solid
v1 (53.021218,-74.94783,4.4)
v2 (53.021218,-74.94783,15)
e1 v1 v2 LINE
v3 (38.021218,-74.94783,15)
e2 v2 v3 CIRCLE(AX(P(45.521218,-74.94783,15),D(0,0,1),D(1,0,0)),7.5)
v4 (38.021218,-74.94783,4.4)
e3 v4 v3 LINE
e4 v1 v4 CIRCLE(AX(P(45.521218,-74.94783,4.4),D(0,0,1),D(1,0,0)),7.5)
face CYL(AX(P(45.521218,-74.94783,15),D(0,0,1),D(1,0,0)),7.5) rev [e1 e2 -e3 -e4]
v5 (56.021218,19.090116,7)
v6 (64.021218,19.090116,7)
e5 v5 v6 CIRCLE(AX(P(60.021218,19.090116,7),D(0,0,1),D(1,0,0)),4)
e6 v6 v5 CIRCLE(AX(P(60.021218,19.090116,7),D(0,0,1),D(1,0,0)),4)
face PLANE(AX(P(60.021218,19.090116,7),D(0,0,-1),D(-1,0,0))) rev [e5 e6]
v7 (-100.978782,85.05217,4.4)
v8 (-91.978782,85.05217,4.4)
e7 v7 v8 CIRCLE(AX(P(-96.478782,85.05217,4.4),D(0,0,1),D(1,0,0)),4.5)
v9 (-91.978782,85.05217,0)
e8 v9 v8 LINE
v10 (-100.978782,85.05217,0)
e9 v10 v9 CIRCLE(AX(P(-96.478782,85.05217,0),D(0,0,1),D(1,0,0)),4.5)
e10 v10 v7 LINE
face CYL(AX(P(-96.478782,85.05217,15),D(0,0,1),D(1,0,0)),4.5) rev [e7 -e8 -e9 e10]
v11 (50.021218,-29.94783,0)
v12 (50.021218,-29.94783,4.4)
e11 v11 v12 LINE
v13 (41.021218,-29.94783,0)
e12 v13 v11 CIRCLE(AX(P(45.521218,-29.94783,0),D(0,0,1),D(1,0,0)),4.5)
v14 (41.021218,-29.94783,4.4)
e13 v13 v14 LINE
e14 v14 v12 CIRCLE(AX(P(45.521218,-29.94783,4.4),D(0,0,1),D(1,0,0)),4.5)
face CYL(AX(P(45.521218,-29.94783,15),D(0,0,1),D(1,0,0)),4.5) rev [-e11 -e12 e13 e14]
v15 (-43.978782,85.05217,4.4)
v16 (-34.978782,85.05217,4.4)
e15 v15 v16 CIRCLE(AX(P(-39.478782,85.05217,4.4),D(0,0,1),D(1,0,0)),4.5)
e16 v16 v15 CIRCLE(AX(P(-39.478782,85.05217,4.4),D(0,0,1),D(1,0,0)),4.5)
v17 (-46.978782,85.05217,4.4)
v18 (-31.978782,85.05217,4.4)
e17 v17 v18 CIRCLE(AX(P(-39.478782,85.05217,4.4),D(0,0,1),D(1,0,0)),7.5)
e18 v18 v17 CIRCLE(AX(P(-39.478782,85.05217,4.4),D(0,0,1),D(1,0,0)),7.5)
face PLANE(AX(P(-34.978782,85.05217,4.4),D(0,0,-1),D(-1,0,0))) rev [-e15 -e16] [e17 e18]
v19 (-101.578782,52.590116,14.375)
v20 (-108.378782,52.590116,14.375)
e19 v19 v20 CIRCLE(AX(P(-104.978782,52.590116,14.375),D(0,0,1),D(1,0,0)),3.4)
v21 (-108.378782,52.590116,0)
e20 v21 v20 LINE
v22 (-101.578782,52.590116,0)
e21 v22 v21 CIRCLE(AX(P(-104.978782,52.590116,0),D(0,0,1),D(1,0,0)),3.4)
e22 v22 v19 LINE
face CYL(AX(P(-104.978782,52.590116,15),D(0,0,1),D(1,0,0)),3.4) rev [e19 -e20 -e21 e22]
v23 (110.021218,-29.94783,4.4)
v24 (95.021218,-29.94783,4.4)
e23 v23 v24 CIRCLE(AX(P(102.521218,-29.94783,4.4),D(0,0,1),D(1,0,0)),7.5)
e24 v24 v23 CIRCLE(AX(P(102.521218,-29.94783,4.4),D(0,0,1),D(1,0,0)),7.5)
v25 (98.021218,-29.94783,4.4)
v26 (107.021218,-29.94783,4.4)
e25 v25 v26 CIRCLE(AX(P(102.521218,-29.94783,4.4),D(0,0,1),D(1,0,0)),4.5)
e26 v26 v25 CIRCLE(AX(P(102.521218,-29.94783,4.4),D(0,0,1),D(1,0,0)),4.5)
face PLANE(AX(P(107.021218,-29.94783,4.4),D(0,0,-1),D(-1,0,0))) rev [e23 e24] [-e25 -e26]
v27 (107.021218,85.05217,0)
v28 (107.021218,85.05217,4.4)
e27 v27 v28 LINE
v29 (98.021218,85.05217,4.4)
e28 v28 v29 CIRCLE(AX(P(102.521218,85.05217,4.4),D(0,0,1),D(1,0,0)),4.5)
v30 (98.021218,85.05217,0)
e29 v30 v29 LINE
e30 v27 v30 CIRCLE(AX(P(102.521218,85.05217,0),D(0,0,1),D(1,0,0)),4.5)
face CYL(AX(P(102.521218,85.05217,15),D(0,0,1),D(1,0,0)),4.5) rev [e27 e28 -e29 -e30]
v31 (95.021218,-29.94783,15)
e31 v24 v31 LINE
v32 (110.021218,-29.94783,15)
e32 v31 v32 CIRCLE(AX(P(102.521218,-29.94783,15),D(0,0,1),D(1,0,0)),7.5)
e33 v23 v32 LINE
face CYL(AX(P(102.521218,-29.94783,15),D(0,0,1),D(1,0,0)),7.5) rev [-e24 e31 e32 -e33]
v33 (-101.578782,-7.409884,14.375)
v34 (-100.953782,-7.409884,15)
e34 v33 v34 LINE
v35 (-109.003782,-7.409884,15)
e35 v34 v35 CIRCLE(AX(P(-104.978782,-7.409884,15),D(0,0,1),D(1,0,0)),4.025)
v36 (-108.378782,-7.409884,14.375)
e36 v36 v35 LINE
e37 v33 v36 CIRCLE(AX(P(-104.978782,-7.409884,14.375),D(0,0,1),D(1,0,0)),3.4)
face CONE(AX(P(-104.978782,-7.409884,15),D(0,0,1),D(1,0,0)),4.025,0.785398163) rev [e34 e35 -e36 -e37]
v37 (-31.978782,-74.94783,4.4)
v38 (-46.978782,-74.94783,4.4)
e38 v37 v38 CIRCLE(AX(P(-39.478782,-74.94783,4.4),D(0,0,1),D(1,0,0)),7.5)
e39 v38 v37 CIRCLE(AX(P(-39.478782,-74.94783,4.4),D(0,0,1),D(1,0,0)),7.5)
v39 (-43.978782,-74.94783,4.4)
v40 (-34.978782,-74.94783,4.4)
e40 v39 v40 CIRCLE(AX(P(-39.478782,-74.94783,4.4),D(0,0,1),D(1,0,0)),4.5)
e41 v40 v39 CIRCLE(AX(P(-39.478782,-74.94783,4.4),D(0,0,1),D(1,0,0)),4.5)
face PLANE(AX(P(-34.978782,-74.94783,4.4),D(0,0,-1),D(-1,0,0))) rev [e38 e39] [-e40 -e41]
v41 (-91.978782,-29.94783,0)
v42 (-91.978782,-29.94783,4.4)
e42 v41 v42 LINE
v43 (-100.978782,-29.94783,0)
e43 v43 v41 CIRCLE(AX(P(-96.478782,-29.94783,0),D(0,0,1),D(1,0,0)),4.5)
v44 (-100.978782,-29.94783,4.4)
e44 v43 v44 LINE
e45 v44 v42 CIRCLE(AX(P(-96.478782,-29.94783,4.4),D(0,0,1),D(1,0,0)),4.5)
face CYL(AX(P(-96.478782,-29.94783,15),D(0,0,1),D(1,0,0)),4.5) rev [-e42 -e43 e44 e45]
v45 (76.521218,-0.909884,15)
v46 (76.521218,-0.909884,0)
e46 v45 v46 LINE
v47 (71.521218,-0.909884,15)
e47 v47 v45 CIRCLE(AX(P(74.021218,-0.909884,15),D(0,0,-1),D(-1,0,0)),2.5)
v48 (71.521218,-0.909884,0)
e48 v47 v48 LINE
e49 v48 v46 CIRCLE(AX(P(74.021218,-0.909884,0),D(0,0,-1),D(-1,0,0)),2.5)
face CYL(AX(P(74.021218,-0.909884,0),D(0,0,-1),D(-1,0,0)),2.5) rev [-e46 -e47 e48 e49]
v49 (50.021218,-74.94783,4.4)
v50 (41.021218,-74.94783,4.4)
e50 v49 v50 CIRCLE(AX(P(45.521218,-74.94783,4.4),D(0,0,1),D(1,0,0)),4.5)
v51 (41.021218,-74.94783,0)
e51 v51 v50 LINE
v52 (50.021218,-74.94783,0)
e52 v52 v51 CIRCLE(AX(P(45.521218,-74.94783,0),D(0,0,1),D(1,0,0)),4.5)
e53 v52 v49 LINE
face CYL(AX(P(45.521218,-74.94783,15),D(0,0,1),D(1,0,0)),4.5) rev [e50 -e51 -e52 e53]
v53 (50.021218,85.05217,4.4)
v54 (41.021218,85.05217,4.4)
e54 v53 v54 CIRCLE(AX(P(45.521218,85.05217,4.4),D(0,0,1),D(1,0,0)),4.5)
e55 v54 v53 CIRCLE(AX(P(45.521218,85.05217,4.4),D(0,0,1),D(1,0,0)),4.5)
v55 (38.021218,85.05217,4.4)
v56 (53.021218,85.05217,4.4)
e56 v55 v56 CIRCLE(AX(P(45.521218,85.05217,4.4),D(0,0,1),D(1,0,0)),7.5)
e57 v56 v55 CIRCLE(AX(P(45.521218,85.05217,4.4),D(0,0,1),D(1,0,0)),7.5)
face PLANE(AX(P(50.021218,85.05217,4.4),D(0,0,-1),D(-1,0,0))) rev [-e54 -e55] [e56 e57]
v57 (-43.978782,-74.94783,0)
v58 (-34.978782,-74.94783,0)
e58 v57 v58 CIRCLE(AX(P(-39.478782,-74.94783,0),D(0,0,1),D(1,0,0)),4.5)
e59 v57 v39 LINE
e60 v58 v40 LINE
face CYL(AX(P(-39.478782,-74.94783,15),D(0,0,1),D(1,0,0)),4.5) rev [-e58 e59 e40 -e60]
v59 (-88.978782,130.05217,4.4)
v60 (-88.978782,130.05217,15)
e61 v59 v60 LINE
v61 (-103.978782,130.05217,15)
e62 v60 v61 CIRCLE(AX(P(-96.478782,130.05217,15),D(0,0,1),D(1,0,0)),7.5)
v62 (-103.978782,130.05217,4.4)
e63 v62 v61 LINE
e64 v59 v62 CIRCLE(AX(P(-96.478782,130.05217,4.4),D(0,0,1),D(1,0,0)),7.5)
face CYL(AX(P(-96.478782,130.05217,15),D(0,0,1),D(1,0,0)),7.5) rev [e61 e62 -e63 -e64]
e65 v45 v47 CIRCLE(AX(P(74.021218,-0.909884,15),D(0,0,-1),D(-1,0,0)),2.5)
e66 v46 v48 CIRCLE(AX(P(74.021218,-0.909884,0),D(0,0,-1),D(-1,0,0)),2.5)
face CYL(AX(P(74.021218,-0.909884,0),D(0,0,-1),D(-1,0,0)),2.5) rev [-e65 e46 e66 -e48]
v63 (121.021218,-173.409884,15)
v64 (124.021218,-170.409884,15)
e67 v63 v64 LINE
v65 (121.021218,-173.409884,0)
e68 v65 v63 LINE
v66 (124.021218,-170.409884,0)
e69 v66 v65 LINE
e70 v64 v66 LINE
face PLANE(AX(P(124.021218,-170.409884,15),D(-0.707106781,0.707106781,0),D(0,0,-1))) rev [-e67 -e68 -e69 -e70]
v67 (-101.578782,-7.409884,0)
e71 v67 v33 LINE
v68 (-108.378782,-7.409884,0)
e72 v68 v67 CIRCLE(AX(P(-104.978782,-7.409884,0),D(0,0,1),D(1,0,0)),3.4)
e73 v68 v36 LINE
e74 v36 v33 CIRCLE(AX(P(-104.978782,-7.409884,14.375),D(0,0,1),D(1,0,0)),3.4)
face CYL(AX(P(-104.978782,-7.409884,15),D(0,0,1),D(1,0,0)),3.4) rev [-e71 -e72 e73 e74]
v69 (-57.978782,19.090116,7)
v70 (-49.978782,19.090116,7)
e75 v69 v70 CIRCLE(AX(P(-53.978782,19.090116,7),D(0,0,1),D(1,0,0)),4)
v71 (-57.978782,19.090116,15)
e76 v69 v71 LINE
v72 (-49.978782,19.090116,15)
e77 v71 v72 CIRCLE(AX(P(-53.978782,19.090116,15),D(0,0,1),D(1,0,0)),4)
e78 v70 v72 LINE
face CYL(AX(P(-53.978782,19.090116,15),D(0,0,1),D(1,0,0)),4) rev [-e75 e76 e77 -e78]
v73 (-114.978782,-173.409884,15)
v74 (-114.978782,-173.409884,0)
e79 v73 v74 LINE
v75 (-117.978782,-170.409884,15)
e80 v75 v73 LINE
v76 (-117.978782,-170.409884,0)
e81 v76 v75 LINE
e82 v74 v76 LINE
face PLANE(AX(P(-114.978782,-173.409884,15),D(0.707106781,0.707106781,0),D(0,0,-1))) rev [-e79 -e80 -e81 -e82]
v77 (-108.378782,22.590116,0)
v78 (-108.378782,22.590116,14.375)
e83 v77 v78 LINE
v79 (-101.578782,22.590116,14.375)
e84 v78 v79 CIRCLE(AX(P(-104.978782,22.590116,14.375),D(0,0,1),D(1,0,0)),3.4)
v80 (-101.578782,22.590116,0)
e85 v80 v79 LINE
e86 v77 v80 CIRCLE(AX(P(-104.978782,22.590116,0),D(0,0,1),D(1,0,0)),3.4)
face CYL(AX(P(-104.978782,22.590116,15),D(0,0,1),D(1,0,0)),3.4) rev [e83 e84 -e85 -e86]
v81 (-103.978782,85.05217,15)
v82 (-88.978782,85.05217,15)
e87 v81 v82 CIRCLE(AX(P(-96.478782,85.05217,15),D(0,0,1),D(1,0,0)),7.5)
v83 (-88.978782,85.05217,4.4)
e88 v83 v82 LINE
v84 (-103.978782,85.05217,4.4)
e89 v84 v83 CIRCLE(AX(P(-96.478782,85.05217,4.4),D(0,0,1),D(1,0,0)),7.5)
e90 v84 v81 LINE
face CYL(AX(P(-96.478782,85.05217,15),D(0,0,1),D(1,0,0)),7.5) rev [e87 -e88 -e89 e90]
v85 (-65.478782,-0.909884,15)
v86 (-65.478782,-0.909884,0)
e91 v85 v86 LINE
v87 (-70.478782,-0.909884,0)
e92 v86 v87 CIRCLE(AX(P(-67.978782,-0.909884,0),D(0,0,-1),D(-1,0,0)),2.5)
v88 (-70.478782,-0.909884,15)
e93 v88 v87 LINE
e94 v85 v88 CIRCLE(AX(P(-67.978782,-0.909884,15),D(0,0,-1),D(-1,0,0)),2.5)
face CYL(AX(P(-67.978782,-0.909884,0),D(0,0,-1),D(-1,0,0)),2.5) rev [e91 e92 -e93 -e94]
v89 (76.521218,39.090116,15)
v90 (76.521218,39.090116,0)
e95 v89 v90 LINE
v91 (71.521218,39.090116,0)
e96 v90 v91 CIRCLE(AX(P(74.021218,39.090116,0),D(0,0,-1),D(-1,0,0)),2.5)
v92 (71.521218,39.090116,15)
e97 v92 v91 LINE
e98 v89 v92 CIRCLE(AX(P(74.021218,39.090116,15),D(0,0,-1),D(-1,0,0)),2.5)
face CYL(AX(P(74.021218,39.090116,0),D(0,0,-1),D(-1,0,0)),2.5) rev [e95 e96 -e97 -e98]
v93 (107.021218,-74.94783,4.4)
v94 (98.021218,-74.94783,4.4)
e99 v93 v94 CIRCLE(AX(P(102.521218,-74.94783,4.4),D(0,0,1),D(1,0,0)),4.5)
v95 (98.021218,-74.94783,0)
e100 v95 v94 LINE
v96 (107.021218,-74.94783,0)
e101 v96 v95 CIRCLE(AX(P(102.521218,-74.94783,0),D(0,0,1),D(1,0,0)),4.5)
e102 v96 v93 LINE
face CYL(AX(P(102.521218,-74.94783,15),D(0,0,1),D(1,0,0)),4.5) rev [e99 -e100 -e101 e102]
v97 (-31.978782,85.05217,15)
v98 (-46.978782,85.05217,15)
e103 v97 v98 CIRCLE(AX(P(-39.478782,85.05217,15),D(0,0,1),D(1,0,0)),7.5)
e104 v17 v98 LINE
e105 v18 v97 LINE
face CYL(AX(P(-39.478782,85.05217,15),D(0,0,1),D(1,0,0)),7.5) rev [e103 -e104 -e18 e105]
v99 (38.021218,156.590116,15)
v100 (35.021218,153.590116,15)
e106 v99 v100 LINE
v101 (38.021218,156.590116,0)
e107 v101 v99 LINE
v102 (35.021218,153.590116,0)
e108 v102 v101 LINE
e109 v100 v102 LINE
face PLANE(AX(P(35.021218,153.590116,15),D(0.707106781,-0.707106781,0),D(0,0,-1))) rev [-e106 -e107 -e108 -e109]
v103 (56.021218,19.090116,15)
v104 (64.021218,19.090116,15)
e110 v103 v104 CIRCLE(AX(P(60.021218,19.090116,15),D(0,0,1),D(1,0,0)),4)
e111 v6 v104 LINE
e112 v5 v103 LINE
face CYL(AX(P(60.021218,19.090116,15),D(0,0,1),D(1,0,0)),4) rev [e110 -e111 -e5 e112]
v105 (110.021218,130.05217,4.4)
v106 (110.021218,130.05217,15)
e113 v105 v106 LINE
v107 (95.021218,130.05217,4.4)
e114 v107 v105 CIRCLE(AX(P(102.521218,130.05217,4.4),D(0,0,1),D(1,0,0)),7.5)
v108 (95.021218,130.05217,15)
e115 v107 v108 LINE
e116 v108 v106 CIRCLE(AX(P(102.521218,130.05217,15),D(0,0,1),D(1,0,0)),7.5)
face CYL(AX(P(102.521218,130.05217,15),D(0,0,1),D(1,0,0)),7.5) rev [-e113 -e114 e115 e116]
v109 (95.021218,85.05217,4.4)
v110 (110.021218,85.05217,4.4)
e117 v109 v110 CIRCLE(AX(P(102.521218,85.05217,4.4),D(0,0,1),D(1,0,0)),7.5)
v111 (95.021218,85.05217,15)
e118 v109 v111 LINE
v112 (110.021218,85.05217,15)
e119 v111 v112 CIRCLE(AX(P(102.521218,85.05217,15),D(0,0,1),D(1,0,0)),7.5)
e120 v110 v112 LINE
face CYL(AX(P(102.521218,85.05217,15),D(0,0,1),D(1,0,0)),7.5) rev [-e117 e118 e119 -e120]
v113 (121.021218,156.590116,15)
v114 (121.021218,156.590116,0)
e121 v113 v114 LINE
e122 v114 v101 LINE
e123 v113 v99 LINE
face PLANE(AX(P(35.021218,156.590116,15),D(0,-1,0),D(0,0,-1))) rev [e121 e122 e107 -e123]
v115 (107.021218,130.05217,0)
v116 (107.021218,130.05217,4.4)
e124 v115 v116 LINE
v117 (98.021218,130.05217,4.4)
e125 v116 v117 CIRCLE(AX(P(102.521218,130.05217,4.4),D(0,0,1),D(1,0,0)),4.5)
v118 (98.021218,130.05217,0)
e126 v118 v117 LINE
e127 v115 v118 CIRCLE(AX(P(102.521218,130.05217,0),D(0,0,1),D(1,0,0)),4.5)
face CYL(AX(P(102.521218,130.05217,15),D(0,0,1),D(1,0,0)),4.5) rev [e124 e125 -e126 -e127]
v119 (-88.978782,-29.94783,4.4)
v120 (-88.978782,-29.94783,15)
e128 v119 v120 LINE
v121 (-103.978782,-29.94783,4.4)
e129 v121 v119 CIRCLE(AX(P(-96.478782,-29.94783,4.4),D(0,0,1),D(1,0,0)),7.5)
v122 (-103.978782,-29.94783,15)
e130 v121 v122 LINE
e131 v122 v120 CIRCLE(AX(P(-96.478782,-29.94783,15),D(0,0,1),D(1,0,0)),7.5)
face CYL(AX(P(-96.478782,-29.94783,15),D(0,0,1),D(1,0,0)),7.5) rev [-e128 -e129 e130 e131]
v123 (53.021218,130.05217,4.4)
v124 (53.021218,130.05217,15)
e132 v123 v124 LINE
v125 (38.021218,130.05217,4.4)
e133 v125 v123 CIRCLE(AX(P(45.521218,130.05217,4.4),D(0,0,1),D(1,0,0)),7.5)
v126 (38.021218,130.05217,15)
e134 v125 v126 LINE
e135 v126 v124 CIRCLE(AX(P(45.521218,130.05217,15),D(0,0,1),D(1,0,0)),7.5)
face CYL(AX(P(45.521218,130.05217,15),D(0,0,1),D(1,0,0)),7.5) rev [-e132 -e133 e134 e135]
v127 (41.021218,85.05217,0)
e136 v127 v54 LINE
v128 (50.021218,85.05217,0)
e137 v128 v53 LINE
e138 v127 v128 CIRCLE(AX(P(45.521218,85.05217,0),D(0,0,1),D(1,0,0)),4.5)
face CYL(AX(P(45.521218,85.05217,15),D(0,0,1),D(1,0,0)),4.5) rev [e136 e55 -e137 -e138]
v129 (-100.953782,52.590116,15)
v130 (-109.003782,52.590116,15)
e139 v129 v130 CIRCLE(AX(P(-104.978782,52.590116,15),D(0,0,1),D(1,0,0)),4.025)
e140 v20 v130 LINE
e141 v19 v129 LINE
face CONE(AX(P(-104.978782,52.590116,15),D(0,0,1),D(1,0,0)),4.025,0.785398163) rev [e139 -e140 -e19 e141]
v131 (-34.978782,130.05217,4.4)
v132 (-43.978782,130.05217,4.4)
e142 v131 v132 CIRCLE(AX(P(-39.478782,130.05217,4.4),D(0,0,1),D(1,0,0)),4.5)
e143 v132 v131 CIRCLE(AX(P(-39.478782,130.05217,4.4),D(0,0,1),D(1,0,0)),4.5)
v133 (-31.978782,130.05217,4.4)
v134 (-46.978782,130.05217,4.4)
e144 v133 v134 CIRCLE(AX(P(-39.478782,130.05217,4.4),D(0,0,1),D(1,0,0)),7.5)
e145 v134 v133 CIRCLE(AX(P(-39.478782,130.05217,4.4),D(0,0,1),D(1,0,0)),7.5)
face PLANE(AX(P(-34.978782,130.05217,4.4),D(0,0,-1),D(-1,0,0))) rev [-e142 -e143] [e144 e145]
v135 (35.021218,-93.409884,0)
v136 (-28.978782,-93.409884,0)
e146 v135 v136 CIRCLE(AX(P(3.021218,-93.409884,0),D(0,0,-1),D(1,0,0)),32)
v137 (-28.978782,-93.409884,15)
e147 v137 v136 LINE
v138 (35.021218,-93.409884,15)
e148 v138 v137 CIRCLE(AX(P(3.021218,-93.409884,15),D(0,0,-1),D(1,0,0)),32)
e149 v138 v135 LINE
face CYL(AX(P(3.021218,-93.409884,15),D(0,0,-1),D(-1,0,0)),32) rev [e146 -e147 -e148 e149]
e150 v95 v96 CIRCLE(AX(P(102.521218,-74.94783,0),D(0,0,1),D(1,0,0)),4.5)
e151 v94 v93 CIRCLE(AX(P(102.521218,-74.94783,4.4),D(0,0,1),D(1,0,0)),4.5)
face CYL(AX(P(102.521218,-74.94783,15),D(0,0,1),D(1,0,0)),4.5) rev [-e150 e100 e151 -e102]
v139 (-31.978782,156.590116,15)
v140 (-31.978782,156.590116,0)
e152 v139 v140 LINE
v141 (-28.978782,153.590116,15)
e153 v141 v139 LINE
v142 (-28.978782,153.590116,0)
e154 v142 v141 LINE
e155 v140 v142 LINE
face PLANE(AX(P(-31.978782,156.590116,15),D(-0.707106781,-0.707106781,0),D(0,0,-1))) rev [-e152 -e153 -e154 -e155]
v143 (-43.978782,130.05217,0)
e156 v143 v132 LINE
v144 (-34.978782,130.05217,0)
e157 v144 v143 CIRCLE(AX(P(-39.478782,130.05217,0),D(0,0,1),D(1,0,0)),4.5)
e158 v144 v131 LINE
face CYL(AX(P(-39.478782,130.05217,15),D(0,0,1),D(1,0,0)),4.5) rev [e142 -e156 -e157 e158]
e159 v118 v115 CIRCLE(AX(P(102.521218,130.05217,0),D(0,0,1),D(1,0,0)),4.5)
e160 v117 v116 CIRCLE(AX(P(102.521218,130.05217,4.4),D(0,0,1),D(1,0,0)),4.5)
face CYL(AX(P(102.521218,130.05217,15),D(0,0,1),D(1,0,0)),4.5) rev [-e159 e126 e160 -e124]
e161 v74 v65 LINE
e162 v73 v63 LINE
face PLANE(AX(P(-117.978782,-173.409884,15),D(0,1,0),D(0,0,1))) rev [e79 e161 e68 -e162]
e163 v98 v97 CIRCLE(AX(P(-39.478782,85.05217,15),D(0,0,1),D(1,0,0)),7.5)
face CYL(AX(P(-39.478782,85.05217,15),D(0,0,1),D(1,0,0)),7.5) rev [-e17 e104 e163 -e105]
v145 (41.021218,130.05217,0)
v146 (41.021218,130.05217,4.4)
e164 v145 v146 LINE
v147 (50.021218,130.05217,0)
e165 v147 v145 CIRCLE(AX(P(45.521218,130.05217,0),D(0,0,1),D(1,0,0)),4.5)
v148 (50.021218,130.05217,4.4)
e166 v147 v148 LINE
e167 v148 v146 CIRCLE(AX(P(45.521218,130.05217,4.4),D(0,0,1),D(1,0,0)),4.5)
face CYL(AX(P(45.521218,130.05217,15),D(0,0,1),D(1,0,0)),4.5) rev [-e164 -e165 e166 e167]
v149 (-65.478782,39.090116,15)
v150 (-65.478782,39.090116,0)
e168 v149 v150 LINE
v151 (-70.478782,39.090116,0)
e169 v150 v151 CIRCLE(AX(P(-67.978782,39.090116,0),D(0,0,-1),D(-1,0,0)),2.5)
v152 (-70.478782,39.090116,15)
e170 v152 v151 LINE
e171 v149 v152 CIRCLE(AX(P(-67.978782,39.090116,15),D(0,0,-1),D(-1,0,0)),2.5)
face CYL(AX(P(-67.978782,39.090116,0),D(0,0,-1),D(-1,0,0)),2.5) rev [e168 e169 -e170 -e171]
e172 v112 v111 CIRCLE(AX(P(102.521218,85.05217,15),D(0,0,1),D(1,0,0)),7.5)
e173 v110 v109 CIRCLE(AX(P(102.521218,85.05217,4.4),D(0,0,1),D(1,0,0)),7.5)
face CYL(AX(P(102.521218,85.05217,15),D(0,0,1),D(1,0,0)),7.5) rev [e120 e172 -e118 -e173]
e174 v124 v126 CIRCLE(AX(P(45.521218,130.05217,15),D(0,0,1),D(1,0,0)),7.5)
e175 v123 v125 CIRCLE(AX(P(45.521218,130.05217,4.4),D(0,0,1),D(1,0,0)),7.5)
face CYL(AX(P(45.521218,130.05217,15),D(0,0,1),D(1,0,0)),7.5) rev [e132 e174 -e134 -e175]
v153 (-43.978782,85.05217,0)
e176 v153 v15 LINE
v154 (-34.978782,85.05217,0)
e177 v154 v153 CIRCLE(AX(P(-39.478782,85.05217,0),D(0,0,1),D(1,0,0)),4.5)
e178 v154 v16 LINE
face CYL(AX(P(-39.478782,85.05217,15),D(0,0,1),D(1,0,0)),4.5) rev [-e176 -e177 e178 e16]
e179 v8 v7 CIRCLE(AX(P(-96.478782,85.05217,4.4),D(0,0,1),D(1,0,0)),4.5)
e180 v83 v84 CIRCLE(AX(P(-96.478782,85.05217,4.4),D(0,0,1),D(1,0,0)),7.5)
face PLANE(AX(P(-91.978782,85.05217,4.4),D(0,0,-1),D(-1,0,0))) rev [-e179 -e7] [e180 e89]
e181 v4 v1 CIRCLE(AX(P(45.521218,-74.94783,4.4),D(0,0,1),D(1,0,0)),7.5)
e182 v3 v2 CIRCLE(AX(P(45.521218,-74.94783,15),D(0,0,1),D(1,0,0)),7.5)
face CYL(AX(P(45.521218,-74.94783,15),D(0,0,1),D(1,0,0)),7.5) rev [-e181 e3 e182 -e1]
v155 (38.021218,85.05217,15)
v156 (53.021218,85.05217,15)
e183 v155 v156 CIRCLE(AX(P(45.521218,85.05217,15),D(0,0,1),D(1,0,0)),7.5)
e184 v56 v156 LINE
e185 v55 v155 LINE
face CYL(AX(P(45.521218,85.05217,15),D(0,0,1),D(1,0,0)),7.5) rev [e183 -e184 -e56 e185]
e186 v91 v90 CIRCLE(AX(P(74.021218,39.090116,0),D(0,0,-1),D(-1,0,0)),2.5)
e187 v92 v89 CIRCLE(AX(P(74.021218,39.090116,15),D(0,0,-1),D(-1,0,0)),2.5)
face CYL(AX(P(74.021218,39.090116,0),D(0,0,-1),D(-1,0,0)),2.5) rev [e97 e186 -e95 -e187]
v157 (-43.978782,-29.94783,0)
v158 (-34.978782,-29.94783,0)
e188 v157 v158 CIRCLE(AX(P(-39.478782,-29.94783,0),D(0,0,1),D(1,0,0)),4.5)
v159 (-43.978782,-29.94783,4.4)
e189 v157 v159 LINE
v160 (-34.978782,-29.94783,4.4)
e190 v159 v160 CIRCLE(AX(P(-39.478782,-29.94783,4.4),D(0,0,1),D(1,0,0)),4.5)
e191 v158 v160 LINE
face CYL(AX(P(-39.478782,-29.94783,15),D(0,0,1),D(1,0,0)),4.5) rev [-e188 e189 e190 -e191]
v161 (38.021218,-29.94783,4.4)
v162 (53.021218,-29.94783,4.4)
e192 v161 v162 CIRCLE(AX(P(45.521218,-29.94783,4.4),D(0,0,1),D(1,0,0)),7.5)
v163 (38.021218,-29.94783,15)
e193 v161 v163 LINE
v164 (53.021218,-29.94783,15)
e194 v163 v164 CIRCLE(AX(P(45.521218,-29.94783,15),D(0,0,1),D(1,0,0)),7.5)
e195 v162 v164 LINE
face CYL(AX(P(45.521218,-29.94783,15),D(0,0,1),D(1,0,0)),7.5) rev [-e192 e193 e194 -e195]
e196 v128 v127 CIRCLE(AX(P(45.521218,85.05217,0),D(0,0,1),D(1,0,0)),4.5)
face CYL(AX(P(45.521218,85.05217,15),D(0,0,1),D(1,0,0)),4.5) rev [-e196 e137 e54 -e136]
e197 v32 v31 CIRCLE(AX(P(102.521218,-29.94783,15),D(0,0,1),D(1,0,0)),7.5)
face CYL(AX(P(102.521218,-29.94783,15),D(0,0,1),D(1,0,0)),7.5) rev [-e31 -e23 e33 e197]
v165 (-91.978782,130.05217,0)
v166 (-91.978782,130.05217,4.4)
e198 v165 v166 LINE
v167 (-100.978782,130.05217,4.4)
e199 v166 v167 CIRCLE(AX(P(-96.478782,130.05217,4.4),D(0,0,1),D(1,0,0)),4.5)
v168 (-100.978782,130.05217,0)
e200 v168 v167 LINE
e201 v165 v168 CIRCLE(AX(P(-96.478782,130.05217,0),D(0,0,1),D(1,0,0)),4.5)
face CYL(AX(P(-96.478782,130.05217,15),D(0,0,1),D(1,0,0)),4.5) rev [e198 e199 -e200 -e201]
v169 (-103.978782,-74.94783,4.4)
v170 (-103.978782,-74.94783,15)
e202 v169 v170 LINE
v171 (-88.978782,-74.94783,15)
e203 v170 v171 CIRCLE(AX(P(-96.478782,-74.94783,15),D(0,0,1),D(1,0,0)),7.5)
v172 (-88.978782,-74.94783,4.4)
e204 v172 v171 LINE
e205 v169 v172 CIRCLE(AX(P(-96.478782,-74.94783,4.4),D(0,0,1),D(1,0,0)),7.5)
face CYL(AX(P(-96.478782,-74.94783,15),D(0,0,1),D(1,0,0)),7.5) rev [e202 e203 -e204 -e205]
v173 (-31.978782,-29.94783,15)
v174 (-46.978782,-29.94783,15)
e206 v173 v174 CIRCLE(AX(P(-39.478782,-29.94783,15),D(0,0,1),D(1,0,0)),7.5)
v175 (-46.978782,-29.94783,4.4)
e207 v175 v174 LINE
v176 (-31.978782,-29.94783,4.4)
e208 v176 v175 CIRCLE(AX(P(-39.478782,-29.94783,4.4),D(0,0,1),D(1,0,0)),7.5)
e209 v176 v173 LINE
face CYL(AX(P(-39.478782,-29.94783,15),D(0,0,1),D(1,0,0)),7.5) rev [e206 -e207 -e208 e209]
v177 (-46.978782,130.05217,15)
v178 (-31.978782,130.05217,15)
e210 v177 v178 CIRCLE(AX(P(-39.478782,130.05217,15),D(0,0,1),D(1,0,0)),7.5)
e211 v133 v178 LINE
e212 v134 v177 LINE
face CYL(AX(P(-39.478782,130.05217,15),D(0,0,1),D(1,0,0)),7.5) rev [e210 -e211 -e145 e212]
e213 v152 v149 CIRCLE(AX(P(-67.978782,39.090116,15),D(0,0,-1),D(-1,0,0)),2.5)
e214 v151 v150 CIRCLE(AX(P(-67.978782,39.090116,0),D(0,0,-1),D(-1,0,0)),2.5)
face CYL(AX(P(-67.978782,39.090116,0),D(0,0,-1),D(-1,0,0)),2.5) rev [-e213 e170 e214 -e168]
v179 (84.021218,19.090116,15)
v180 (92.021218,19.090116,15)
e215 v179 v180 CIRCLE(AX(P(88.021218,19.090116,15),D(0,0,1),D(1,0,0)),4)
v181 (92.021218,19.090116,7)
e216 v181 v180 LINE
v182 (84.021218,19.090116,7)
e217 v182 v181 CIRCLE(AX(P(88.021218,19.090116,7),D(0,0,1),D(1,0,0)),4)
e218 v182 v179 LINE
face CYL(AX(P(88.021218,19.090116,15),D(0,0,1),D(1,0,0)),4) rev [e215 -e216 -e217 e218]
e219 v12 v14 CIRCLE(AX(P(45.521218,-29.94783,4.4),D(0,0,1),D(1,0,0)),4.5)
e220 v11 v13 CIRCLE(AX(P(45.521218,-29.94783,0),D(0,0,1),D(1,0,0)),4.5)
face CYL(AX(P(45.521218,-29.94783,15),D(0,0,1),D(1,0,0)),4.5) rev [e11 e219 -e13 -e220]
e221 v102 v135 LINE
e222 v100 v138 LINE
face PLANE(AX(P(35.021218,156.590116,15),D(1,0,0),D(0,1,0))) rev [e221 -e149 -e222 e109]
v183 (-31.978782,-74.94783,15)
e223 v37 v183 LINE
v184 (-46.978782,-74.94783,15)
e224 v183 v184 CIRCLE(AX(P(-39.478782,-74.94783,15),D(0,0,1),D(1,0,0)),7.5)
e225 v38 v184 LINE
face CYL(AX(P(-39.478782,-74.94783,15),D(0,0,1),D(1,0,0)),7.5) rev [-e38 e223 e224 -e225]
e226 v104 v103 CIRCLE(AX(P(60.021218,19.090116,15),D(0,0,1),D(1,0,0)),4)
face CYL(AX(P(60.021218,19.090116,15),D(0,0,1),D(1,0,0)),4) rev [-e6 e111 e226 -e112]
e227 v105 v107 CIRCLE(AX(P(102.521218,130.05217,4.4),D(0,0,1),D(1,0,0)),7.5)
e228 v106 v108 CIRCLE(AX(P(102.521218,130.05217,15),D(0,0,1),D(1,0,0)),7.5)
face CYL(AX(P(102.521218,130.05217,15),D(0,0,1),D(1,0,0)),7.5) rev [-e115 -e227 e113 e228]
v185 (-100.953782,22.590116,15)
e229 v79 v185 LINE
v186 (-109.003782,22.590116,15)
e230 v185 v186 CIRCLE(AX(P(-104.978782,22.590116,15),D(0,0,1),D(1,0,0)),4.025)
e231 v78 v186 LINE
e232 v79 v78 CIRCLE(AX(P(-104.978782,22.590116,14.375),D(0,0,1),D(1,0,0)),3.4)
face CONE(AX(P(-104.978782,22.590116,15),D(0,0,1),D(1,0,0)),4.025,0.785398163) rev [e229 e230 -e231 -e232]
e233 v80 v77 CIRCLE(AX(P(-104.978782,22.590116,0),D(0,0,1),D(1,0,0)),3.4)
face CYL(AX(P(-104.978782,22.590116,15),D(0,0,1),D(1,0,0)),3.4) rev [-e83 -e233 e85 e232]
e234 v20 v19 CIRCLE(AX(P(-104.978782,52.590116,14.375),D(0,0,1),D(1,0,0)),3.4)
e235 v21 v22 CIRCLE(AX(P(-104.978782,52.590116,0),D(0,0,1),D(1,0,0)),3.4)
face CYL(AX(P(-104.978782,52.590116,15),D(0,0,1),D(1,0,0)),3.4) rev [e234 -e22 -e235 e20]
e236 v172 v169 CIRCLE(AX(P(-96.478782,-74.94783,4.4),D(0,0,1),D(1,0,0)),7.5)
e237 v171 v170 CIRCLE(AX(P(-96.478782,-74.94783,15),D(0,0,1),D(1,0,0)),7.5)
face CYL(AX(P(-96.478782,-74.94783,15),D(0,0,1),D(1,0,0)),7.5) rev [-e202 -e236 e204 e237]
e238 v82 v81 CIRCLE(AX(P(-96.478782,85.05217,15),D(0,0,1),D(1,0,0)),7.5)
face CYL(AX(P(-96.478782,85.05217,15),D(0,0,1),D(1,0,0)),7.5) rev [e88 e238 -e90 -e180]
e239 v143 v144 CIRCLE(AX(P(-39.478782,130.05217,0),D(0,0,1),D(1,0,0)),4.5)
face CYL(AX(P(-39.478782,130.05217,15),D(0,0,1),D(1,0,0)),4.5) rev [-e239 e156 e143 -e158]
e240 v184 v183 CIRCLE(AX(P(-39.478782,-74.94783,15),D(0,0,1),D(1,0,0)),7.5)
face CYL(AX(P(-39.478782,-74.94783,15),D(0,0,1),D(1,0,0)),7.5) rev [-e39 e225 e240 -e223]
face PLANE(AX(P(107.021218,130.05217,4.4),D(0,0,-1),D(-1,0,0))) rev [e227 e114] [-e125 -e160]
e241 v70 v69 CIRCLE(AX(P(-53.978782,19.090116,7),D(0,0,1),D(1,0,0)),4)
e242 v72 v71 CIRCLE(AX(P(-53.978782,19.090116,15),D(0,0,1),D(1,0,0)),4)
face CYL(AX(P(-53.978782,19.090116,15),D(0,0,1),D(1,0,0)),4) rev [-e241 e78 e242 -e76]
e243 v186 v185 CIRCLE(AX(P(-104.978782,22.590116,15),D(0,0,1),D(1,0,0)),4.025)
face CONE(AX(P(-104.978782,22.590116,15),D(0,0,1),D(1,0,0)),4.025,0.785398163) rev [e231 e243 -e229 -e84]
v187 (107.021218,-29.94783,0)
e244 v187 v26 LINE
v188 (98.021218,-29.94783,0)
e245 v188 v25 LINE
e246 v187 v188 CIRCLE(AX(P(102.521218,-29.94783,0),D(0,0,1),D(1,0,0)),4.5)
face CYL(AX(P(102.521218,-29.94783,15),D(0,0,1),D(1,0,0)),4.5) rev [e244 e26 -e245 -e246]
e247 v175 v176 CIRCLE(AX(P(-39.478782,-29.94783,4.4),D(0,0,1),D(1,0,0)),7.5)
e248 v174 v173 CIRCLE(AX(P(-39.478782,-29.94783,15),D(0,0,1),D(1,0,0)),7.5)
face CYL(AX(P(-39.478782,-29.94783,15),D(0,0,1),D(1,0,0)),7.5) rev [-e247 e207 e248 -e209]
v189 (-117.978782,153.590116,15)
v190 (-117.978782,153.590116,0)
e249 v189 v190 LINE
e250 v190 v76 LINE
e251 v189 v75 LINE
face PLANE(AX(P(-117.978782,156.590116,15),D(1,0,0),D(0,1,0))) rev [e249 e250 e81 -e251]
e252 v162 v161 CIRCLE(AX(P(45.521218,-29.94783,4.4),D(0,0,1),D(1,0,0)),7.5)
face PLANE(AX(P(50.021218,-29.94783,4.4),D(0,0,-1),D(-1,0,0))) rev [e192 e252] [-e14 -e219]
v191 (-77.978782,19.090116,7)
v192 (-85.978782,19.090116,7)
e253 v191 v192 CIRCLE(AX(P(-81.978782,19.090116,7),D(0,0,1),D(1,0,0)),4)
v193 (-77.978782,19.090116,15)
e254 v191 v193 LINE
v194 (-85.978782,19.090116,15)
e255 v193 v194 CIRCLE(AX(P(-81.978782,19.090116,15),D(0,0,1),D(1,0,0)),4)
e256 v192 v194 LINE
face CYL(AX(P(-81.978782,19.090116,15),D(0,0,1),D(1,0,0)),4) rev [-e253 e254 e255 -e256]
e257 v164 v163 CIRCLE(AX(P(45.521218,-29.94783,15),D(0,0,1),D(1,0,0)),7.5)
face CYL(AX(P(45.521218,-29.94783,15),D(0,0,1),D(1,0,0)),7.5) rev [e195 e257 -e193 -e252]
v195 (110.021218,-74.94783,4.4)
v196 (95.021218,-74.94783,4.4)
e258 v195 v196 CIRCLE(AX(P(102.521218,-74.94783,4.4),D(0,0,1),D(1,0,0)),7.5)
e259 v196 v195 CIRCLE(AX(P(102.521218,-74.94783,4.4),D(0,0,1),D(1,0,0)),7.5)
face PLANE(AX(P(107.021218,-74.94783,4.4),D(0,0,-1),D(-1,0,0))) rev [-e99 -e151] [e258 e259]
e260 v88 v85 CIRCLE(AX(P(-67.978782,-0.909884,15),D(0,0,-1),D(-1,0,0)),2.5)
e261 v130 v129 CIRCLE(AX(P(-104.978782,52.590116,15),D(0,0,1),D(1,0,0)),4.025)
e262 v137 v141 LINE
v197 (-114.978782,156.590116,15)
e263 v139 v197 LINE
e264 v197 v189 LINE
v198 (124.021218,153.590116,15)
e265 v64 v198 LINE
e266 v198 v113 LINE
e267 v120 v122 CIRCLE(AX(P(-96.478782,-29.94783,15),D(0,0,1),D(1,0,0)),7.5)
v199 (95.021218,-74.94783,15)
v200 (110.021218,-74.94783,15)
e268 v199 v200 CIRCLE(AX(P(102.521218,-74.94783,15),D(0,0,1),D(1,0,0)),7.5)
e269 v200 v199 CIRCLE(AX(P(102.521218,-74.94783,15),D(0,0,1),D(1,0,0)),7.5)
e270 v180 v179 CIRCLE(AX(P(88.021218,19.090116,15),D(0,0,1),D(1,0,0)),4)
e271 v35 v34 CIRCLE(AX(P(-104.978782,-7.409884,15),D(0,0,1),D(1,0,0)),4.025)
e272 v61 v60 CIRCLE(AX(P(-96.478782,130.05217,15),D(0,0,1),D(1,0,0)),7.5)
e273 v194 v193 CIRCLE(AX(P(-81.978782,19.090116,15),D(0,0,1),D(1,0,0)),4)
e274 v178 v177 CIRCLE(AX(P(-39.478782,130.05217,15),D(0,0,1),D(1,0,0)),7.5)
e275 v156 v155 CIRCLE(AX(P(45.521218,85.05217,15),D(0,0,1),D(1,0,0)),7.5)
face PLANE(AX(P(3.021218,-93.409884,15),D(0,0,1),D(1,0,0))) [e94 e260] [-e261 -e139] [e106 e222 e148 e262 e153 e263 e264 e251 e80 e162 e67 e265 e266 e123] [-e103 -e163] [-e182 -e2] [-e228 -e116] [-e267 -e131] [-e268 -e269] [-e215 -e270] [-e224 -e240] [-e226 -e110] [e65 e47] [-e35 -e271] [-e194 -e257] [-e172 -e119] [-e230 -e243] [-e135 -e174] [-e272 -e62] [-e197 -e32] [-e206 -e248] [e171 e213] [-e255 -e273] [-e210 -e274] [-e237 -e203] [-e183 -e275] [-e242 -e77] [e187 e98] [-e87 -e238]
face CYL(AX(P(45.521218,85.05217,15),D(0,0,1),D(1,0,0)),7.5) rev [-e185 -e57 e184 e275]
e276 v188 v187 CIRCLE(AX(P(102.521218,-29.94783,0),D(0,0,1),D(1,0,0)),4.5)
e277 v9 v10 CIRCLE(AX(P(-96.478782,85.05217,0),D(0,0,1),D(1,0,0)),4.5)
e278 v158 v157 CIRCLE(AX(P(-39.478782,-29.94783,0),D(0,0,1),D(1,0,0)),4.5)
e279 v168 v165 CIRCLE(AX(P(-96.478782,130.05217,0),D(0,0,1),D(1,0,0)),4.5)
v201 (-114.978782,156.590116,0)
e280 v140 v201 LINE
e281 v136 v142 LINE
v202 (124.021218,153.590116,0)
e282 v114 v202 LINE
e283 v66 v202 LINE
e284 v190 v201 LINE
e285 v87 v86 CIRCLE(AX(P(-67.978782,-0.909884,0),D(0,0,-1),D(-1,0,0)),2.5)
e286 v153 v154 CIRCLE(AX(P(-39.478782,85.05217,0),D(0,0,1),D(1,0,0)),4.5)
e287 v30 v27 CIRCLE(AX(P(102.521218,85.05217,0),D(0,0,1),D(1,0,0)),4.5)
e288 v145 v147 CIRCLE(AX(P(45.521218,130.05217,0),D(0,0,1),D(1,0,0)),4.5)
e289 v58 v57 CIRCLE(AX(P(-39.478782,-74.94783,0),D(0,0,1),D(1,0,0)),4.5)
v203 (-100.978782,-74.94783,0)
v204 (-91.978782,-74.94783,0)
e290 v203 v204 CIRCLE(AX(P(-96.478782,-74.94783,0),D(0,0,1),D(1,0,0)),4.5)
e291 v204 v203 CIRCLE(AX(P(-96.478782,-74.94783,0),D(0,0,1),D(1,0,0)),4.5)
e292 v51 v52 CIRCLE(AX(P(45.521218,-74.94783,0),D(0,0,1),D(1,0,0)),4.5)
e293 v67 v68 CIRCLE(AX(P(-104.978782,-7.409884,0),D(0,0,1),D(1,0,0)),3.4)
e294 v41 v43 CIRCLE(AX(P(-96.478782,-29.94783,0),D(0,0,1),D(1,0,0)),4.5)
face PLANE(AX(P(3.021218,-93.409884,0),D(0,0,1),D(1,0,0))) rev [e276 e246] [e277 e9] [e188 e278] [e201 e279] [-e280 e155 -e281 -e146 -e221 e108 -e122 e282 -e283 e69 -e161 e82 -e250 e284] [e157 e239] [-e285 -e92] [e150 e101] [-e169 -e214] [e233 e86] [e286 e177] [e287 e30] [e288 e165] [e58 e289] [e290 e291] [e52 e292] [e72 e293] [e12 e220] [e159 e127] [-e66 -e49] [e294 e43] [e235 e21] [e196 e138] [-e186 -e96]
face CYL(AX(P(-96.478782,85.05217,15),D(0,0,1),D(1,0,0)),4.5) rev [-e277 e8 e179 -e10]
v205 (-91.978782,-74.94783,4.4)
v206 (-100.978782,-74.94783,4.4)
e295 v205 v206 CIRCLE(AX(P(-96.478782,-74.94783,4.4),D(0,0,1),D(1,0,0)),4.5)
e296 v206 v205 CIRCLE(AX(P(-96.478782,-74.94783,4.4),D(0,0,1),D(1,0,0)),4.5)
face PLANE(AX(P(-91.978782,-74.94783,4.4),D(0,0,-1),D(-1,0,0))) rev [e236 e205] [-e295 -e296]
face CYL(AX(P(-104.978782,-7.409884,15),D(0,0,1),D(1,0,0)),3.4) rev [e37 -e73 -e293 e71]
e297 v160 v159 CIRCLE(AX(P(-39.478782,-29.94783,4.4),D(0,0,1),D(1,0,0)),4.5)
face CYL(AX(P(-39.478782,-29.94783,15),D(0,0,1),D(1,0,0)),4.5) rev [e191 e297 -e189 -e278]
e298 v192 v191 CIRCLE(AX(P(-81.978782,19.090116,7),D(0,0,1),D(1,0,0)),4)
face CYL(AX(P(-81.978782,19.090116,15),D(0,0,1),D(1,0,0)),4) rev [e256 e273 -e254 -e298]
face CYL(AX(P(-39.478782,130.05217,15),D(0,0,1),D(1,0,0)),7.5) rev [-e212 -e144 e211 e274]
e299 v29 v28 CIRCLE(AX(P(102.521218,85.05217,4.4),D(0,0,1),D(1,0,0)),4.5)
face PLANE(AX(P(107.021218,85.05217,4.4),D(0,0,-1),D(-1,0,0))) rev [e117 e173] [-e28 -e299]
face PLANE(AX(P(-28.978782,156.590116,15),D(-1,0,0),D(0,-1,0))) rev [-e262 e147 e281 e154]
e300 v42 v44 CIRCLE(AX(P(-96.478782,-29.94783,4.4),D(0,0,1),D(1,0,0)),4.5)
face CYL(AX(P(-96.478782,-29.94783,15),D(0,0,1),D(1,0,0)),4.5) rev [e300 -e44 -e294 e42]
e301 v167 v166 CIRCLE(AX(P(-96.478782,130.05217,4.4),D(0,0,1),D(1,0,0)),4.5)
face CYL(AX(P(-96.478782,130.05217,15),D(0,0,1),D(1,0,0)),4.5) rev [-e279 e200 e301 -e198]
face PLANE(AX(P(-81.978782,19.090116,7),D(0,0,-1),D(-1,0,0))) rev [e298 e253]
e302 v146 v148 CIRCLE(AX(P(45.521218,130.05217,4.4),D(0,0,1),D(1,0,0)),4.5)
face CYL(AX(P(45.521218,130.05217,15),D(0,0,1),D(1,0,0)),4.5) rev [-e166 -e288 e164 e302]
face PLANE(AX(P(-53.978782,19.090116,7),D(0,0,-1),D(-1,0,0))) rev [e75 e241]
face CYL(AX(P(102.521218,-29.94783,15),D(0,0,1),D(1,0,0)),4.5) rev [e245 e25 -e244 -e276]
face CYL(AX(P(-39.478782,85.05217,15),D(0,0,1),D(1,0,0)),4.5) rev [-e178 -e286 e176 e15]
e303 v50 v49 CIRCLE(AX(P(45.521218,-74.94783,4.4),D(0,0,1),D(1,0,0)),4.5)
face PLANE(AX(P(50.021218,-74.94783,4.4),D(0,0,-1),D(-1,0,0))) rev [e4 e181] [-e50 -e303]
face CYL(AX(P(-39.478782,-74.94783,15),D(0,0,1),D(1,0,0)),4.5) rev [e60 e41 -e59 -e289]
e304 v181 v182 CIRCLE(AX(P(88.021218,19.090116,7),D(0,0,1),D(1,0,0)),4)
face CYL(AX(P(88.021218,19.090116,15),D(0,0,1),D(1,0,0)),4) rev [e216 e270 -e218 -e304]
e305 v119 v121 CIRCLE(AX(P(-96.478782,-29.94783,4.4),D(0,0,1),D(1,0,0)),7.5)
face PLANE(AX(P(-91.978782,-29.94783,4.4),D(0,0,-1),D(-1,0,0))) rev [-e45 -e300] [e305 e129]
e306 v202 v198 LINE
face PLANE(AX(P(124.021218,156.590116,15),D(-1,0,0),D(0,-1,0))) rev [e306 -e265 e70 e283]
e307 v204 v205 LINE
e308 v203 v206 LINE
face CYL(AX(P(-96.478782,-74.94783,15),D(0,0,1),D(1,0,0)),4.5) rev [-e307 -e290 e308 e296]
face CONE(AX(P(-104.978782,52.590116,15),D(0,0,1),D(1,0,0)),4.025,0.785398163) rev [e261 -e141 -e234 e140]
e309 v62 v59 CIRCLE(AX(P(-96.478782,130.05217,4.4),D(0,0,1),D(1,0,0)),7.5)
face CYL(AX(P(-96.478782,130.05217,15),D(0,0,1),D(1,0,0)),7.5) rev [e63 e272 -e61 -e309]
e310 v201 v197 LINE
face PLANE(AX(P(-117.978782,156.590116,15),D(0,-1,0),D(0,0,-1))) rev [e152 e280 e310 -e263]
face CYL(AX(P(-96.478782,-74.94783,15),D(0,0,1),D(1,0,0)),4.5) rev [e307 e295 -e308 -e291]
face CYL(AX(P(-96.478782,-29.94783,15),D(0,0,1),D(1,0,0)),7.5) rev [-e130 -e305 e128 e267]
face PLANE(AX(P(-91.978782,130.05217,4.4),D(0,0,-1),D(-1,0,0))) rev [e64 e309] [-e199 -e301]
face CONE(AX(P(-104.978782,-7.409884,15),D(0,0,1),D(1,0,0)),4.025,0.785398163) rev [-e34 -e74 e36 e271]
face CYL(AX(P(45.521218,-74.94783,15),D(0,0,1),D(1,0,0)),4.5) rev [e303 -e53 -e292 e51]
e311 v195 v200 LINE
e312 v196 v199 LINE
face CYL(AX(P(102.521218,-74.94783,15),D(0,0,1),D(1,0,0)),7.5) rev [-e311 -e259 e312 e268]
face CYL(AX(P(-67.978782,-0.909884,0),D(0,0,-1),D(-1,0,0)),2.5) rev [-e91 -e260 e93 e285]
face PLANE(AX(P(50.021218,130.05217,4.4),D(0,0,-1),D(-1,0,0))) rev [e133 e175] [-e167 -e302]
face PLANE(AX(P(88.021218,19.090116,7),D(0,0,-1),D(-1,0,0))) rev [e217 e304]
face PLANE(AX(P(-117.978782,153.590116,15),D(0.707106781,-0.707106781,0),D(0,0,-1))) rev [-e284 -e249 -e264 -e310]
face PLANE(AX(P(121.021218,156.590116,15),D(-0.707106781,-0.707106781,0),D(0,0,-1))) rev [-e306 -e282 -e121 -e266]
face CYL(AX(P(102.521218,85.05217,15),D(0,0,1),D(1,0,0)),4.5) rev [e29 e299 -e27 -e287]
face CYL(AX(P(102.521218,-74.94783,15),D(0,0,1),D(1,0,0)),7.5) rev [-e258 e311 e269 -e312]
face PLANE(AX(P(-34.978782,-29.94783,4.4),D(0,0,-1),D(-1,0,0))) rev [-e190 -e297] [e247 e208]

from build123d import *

# Parameters (mm, degrees)
BOSS_EXTRUDE1_DEPTH         = 15
CHAMFER1_SIZE               = 3
HOLE1_D                     = 9
HOLE1_CBORE_D               = 15
HOLE1_CBORE_DEPTH           = 10.6
M8_TAPPED_HOLE1_D           = 6.8
M8_TAPPED_HOLE1_CSINK_D     = 8.05
M8_TAPPED_HOLE1_CSINK_ANGLE = 90
HOLE2_D                     = 8
HOLE2_DEPTH                 = 8
M6_TAPPED_HOLE1_D           = 5


with BuildPart() as part:
    # Sketch1 → Boss-Extrude1 (new body)
    with BuildSketch(Plane.XY):
        with BuildLine():
            Line((-117.978782331, 156.590116279), (-28.978782331, 156.590116279))
            Line((-28.978782331, 156.590116279), (-28.978782331, -93.409883721))
            ThreePointArc((-28.978782331, -93.409883721), (3.021217669, -125.409883721), (35.021217669, -93.409883721))
            Line((35.021217669, -93.409883721), (35.021217669, 156.590116279))
            Line((35.021217669, 156.590116279), (124.021217669, 156.590116279))
            Line((124.021217669, 156.590116279), (124.021217669, -173.409883721))
            Line((124.021217669, -173.409883721), (-117.978782331, -173.409883721))
            Line((-117.978782331, -173.409883721), (-117.978782331, 156.590116279))
        make_face()
    extrude(amount=BOSS_EXTRUDE1_DEPTH)

    # Chamfer1
    chamfer1_edges = [part.edges().sort_by_distance(p)[0] for p in [
        (-117.978782331, 156.590116279, 7.5),
        (-28.978782331, 156.590116279, 7.5),
        (35.021217669, 156.590116279, 7.5),
        (124.021217669, 156.590116279, 7.5),
        (124.021217669, -173.409883721, 7.5),
        (-117.978782331, -173.409883721, 7.5),
    ]]
    chamfer(chamfer1_edges, length=CHAMFER1_SIZE)

    # Hole1 (through all)
    with Locations(Plane.XY.offset(15)):
        with Locations((-96.478782331, 130.052169647), (-39.478782331, 130.052169647), (-39.478782331, 85.052169647), (-96.478782331, 85.052169647), (-96.478782331, -29.947830353), (-39.478782331, -29.947830353), (-39.478782331, -74.947830353), (-96.478782331, -74.947830353), (45.521217669, -74.947830353), (45.521217669, -29.947830353), (102.521217669, -29.947830353), (102.521217669, -74.947830353), (45.521217669, 85.052169647), (45.521217669, 130.052169647), (102.521217669, 130.052169647), (102.521217669, 85.052169647)):
            CounterBoreHole(HOLE1_D / 2, HOLE1_CBORE_D / 2, HOLE1_CBORE_DEPTH)

    # M8 Tapped Hole1 (through all)
    with Locations(Plane.XY.offset(15)):
        with Locations((-104.978782331, 52.590116279), (-104.978782331, 22.590116279), (-104.978782331, -7.409883721)):
            CounterSinkHole(M8_TAPPED_HOLE1_D / 2, M8_TAPPED_HOLE1_CSINK_D / 2, counter_sink_angle=M8_TAPPED_HOLE1_CSINK_ANGLE)

    # Hole2
    with Locations(Plane.XY.offset(15)):
        with Locations((-81.978782331, 19.090116279), (-53.978782331, 19.090116279), (60.021217669, 19.090116279), (88.021217669, 19.090116279)):
            Hole(HOLE2_D / 2, depth=HOLE2_DEPTH)

    # M6 Tapped Hole1 (through all)
    with Locations(Plane(origin=(0, 0, 0), x_dir=(-1, 0, 0), z_dir=(0, 0, -1))):
        with Locations((-74.021217669, 39.090116279), (-74.021217669, -0.909883721), (67.978782331, -0.909883721), (67.978782331, 39.090116279)):
            Hole(M6_TAPPED_HOLE1_D / 2)


solid = part.part
